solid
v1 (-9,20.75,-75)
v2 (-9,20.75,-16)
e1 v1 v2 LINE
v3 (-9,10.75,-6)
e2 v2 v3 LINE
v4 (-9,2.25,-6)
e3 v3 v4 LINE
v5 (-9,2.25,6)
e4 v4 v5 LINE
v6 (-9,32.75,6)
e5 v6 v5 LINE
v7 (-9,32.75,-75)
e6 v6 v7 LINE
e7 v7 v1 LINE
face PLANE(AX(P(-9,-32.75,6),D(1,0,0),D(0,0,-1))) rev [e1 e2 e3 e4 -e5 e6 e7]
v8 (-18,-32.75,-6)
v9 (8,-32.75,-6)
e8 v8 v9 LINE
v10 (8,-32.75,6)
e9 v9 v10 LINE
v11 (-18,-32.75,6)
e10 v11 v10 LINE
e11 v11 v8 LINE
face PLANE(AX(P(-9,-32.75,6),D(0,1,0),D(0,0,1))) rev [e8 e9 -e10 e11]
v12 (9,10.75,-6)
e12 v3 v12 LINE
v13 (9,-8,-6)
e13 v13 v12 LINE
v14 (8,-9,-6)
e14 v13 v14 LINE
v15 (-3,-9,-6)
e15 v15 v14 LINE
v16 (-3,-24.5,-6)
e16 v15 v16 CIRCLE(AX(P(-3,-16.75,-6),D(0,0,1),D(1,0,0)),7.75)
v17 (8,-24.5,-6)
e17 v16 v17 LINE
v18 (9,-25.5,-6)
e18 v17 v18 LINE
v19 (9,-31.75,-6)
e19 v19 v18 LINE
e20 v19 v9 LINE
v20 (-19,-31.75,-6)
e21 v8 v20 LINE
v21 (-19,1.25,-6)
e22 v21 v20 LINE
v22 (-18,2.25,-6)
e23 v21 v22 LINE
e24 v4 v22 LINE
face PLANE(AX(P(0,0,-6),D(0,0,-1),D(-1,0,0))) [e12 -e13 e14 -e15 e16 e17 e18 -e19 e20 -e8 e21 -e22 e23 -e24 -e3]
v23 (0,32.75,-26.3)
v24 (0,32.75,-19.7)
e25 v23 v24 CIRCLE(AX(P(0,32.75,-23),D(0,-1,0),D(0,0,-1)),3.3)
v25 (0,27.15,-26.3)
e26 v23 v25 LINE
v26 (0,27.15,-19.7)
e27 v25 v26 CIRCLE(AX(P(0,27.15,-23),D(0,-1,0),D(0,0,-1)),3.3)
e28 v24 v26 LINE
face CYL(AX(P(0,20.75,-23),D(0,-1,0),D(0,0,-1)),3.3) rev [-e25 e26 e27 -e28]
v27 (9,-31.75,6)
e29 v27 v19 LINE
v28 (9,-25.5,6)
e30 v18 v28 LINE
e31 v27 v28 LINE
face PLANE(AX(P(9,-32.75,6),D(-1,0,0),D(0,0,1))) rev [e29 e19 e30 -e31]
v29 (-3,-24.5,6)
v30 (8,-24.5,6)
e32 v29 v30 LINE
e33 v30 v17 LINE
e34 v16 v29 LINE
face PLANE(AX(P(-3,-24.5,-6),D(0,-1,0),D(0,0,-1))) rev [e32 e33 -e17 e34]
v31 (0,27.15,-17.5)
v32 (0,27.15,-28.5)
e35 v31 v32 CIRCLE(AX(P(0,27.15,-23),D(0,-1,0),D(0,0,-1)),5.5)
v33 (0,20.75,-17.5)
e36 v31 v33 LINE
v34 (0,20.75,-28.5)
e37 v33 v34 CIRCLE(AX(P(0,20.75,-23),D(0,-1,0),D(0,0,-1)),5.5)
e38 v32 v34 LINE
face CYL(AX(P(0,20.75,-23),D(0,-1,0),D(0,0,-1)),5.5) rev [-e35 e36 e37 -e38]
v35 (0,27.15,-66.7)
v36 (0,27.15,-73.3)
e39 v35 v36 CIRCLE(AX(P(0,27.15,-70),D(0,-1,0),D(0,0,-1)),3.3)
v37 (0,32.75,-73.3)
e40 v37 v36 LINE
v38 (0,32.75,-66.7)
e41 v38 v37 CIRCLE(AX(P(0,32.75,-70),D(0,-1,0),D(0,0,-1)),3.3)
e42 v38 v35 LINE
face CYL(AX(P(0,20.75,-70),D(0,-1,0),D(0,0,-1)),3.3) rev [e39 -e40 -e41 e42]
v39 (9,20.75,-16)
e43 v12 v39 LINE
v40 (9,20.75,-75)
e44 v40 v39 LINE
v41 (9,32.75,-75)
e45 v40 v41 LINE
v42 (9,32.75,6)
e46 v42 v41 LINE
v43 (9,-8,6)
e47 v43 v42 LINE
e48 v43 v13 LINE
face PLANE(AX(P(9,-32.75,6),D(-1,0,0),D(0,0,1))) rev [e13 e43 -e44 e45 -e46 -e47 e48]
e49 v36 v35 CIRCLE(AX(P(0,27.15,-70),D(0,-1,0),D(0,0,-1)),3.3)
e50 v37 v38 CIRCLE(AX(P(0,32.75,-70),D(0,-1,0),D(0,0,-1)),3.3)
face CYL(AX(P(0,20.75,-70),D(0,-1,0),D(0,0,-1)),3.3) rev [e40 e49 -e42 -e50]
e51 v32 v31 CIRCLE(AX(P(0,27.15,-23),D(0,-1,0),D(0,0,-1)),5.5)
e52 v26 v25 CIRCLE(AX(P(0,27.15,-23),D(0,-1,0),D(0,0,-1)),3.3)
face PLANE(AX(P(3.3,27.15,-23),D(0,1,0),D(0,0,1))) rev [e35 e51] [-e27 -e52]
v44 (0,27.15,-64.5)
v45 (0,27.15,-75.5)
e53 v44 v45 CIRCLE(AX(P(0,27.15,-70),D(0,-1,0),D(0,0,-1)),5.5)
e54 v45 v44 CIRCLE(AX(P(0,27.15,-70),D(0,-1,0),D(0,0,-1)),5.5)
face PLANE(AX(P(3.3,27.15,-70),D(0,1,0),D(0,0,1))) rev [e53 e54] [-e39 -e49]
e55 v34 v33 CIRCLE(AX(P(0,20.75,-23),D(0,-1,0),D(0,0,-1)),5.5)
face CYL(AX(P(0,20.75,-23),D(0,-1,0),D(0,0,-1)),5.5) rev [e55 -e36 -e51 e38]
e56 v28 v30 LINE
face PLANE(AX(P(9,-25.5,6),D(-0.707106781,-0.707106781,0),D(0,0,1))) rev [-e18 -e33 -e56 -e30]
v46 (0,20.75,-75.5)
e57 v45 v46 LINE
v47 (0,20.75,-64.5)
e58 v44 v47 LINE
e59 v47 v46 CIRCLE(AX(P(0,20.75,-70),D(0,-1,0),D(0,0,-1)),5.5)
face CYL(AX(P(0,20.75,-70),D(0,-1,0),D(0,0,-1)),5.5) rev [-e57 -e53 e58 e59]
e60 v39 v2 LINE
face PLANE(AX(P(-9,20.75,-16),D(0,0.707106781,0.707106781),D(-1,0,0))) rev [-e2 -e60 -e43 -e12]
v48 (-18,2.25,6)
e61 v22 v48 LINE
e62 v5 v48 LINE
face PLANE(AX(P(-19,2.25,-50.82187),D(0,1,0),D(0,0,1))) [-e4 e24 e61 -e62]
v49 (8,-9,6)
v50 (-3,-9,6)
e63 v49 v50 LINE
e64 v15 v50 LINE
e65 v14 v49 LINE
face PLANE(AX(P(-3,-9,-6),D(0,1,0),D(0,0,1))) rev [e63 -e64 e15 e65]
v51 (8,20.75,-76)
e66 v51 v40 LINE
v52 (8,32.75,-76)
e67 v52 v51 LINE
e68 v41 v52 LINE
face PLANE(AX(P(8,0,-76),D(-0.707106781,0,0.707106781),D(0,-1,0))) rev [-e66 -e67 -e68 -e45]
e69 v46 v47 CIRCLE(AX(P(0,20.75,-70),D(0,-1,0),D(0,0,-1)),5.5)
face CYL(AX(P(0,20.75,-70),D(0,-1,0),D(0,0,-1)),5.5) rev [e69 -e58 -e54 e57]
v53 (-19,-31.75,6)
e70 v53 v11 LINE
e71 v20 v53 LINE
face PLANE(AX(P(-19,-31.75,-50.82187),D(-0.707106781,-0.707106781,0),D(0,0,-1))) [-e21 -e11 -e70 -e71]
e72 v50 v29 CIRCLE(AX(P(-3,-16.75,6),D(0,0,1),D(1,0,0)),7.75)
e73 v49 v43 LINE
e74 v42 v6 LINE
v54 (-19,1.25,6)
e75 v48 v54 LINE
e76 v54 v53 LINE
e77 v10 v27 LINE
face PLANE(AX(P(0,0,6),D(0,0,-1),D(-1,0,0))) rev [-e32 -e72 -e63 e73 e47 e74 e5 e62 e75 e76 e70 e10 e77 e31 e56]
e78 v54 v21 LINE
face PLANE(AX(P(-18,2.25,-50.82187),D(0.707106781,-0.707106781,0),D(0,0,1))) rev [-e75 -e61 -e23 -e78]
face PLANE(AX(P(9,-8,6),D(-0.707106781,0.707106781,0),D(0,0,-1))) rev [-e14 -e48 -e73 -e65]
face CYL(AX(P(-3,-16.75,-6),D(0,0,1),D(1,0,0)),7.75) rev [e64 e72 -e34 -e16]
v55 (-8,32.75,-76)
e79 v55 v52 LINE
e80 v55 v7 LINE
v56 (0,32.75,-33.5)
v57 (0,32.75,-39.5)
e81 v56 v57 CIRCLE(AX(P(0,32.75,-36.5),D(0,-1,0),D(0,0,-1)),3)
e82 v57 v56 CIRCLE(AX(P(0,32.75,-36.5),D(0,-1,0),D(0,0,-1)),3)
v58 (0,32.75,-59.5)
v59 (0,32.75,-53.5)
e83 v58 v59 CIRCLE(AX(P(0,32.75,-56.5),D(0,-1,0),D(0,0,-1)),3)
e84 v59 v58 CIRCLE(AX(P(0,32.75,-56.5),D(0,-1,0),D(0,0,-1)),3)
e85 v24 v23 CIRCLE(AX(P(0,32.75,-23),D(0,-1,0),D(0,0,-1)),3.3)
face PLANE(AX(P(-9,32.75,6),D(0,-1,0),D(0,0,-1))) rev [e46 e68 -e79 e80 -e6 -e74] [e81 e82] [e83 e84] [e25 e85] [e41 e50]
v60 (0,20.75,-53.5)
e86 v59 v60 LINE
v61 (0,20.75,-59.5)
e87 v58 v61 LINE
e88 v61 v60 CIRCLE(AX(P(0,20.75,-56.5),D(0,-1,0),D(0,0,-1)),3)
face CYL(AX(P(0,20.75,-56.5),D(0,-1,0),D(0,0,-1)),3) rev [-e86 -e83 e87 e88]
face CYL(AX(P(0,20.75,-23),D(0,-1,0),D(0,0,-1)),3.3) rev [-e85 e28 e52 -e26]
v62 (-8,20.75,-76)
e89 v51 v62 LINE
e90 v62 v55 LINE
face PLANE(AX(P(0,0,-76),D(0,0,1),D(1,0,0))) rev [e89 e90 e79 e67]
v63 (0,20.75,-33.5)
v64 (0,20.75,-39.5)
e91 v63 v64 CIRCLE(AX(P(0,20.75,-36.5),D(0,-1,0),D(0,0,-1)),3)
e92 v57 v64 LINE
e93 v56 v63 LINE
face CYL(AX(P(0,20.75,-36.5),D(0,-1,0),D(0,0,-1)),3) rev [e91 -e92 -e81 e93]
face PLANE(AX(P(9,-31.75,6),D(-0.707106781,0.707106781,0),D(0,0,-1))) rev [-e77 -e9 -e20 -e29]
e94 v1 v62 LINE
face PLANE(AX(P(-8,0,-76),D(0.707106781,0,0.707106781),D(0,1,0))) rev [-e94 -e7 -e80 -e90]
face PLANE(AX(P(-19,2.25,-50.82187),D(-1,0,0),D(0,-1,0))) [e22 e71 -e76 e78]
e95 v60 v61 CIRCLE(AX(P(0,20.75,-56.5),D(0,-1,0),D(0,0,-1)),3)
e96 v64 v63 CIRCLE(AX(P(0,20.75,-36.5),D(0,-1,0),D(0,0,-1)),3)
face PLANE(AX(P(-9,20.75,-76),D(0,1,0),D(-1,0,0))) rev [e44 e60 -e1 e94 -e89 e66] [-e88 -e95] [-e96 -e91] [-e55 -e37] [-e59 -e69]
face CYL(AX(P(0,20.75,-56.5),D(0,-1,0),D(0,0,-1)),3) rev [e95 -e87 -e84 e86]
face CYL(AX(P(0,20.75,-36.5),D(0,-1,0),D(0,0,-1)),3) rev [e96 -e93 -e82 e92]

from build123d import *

# Parameters (mm, degrees)
SKETCH_1_W                   = 18
SKETCH_1_H                   = 65.5
EXTRUDE_1_DEPTH              = 6
SKETCH_2_W                   = 28
SKETCH_2_H                   = 35
EXTRUDE_2_DEPTH              = 12
CUT_EXTRUDE_1_DEPTH          = 40.71854101
SKETCH_4_W                   = 18
SKETCH_4_H                   = 12
EXTRUDE_3_DEPTH              = 70
CHAMFER_1_SIZE               = 10
HOLE_WIZARD_M6_1_D           = 6.6
HOLE_WIZARD_M6_1_CBORE_D     = 11
HOLE_WIZARD_M6_1_CBORE_DEPTH = 6.4
F_6_0MM_1_D                  = 6
CHAMFER_2_SIZE               = 1


with BuildPart() as part:
    # 草图1 → 凸台-拉伸1 (new, symmetric)
    with BuildSketch(Plane.XY):
        Rectangle(SKETCH_1_W, SKETCH_1_H)
    extrude(amount=EXTRUDE_1_DEPTH, both=True)

    # 草图2 → 凸台-拉伸2 (add)
    with BuildSketch(Plane.XY.offset(6)):
        with Locations((-5, -15.25)):
            Rectangle(SKETCH_2_W, SKETCH_2_H)
    extrude(amount=-EXTRUDE_2_DEPTH)

    # 草图3 → 切除-拉伸1 (cut, through all)
    with BuildSketch(Plane.XY.offset(6)):
        with BuildLine():
            Line((-3, -9), (21, -9))
            ThreePointArc((21, -9), (28.75, -16.75), (21, -24.5))
            Line((21, -24.5), (-3, -24.5))
            ThreePointArc((-3, -24.5), (-10.75, -16.75), (-3, -9))
        make_face()
    extrude(amount=-CUT_EXTRUDE_1_DEPTH, mode=Mode.SUBTRACT)

    # 草图4 → 凸台-拉伸3 (add)
    with BuildSketch(Plane(origin=(0, 0, -6), x_dir=(-1, 0, 0), z_dir=(0, 0, -1))):
        with Locations((0, 26.75)):
            Rectangle(SKETCH_4_W, SKETCH_4_H)
    extrude(amount=EXTRUDE_3_DEPTH)

    # 倒角1
    chamfer_1_edges = [part.edges().sort_by_distance(p)[0] for p in [
        (0, 20.75, -6),
    ]]
    chamfer(chamfer_1_edges, length=CHAMFER_1_SIZE)

    # M6 六角凹头螺钉的柱形沉头孔1 (through all)
    with Locations(Plane(origin=(0, 20.75, 0), x_dir=(-1, 0, 0), z_dir=(0, -1, 0))):
        with Locations((0, 23), (0, 70)):
            CounterBoreHole(HOLE_WIZARD_M6_1_D / 2, HOLE_WIZARD_M6_1_CBORE_D / 2, HOLE_WIZARD_M6_1_CBORE_DEPTH)

    # Ø6.0mm 暗销孔1 (through all)
    with Locations(Plane(origin=(0, 20.75, 0), x_dir=(-1, 0, 0), z_dir=(0, -1, 0))):
        with Locations((0, 36.5), (0, 56.5)):
            Hole(F_6_0MM_1_D / 2)

    # 倒角2
    chamfer_2_edges = [part.edges().sort_by_distance(p)[0] for p in [
        (-19, 2.25, 0),
        (-19, -32.75, 0),
        (9, -9, 0),
        (9, -24.5, 0),
        (-9, 26.75, -76),
        (9, 26.75, -76),
        (9, -32.75, 0),
    ]]
    chamfer(chamfer_2_edges, length=CHAMFER_2_SIZE)


solid = part.part
